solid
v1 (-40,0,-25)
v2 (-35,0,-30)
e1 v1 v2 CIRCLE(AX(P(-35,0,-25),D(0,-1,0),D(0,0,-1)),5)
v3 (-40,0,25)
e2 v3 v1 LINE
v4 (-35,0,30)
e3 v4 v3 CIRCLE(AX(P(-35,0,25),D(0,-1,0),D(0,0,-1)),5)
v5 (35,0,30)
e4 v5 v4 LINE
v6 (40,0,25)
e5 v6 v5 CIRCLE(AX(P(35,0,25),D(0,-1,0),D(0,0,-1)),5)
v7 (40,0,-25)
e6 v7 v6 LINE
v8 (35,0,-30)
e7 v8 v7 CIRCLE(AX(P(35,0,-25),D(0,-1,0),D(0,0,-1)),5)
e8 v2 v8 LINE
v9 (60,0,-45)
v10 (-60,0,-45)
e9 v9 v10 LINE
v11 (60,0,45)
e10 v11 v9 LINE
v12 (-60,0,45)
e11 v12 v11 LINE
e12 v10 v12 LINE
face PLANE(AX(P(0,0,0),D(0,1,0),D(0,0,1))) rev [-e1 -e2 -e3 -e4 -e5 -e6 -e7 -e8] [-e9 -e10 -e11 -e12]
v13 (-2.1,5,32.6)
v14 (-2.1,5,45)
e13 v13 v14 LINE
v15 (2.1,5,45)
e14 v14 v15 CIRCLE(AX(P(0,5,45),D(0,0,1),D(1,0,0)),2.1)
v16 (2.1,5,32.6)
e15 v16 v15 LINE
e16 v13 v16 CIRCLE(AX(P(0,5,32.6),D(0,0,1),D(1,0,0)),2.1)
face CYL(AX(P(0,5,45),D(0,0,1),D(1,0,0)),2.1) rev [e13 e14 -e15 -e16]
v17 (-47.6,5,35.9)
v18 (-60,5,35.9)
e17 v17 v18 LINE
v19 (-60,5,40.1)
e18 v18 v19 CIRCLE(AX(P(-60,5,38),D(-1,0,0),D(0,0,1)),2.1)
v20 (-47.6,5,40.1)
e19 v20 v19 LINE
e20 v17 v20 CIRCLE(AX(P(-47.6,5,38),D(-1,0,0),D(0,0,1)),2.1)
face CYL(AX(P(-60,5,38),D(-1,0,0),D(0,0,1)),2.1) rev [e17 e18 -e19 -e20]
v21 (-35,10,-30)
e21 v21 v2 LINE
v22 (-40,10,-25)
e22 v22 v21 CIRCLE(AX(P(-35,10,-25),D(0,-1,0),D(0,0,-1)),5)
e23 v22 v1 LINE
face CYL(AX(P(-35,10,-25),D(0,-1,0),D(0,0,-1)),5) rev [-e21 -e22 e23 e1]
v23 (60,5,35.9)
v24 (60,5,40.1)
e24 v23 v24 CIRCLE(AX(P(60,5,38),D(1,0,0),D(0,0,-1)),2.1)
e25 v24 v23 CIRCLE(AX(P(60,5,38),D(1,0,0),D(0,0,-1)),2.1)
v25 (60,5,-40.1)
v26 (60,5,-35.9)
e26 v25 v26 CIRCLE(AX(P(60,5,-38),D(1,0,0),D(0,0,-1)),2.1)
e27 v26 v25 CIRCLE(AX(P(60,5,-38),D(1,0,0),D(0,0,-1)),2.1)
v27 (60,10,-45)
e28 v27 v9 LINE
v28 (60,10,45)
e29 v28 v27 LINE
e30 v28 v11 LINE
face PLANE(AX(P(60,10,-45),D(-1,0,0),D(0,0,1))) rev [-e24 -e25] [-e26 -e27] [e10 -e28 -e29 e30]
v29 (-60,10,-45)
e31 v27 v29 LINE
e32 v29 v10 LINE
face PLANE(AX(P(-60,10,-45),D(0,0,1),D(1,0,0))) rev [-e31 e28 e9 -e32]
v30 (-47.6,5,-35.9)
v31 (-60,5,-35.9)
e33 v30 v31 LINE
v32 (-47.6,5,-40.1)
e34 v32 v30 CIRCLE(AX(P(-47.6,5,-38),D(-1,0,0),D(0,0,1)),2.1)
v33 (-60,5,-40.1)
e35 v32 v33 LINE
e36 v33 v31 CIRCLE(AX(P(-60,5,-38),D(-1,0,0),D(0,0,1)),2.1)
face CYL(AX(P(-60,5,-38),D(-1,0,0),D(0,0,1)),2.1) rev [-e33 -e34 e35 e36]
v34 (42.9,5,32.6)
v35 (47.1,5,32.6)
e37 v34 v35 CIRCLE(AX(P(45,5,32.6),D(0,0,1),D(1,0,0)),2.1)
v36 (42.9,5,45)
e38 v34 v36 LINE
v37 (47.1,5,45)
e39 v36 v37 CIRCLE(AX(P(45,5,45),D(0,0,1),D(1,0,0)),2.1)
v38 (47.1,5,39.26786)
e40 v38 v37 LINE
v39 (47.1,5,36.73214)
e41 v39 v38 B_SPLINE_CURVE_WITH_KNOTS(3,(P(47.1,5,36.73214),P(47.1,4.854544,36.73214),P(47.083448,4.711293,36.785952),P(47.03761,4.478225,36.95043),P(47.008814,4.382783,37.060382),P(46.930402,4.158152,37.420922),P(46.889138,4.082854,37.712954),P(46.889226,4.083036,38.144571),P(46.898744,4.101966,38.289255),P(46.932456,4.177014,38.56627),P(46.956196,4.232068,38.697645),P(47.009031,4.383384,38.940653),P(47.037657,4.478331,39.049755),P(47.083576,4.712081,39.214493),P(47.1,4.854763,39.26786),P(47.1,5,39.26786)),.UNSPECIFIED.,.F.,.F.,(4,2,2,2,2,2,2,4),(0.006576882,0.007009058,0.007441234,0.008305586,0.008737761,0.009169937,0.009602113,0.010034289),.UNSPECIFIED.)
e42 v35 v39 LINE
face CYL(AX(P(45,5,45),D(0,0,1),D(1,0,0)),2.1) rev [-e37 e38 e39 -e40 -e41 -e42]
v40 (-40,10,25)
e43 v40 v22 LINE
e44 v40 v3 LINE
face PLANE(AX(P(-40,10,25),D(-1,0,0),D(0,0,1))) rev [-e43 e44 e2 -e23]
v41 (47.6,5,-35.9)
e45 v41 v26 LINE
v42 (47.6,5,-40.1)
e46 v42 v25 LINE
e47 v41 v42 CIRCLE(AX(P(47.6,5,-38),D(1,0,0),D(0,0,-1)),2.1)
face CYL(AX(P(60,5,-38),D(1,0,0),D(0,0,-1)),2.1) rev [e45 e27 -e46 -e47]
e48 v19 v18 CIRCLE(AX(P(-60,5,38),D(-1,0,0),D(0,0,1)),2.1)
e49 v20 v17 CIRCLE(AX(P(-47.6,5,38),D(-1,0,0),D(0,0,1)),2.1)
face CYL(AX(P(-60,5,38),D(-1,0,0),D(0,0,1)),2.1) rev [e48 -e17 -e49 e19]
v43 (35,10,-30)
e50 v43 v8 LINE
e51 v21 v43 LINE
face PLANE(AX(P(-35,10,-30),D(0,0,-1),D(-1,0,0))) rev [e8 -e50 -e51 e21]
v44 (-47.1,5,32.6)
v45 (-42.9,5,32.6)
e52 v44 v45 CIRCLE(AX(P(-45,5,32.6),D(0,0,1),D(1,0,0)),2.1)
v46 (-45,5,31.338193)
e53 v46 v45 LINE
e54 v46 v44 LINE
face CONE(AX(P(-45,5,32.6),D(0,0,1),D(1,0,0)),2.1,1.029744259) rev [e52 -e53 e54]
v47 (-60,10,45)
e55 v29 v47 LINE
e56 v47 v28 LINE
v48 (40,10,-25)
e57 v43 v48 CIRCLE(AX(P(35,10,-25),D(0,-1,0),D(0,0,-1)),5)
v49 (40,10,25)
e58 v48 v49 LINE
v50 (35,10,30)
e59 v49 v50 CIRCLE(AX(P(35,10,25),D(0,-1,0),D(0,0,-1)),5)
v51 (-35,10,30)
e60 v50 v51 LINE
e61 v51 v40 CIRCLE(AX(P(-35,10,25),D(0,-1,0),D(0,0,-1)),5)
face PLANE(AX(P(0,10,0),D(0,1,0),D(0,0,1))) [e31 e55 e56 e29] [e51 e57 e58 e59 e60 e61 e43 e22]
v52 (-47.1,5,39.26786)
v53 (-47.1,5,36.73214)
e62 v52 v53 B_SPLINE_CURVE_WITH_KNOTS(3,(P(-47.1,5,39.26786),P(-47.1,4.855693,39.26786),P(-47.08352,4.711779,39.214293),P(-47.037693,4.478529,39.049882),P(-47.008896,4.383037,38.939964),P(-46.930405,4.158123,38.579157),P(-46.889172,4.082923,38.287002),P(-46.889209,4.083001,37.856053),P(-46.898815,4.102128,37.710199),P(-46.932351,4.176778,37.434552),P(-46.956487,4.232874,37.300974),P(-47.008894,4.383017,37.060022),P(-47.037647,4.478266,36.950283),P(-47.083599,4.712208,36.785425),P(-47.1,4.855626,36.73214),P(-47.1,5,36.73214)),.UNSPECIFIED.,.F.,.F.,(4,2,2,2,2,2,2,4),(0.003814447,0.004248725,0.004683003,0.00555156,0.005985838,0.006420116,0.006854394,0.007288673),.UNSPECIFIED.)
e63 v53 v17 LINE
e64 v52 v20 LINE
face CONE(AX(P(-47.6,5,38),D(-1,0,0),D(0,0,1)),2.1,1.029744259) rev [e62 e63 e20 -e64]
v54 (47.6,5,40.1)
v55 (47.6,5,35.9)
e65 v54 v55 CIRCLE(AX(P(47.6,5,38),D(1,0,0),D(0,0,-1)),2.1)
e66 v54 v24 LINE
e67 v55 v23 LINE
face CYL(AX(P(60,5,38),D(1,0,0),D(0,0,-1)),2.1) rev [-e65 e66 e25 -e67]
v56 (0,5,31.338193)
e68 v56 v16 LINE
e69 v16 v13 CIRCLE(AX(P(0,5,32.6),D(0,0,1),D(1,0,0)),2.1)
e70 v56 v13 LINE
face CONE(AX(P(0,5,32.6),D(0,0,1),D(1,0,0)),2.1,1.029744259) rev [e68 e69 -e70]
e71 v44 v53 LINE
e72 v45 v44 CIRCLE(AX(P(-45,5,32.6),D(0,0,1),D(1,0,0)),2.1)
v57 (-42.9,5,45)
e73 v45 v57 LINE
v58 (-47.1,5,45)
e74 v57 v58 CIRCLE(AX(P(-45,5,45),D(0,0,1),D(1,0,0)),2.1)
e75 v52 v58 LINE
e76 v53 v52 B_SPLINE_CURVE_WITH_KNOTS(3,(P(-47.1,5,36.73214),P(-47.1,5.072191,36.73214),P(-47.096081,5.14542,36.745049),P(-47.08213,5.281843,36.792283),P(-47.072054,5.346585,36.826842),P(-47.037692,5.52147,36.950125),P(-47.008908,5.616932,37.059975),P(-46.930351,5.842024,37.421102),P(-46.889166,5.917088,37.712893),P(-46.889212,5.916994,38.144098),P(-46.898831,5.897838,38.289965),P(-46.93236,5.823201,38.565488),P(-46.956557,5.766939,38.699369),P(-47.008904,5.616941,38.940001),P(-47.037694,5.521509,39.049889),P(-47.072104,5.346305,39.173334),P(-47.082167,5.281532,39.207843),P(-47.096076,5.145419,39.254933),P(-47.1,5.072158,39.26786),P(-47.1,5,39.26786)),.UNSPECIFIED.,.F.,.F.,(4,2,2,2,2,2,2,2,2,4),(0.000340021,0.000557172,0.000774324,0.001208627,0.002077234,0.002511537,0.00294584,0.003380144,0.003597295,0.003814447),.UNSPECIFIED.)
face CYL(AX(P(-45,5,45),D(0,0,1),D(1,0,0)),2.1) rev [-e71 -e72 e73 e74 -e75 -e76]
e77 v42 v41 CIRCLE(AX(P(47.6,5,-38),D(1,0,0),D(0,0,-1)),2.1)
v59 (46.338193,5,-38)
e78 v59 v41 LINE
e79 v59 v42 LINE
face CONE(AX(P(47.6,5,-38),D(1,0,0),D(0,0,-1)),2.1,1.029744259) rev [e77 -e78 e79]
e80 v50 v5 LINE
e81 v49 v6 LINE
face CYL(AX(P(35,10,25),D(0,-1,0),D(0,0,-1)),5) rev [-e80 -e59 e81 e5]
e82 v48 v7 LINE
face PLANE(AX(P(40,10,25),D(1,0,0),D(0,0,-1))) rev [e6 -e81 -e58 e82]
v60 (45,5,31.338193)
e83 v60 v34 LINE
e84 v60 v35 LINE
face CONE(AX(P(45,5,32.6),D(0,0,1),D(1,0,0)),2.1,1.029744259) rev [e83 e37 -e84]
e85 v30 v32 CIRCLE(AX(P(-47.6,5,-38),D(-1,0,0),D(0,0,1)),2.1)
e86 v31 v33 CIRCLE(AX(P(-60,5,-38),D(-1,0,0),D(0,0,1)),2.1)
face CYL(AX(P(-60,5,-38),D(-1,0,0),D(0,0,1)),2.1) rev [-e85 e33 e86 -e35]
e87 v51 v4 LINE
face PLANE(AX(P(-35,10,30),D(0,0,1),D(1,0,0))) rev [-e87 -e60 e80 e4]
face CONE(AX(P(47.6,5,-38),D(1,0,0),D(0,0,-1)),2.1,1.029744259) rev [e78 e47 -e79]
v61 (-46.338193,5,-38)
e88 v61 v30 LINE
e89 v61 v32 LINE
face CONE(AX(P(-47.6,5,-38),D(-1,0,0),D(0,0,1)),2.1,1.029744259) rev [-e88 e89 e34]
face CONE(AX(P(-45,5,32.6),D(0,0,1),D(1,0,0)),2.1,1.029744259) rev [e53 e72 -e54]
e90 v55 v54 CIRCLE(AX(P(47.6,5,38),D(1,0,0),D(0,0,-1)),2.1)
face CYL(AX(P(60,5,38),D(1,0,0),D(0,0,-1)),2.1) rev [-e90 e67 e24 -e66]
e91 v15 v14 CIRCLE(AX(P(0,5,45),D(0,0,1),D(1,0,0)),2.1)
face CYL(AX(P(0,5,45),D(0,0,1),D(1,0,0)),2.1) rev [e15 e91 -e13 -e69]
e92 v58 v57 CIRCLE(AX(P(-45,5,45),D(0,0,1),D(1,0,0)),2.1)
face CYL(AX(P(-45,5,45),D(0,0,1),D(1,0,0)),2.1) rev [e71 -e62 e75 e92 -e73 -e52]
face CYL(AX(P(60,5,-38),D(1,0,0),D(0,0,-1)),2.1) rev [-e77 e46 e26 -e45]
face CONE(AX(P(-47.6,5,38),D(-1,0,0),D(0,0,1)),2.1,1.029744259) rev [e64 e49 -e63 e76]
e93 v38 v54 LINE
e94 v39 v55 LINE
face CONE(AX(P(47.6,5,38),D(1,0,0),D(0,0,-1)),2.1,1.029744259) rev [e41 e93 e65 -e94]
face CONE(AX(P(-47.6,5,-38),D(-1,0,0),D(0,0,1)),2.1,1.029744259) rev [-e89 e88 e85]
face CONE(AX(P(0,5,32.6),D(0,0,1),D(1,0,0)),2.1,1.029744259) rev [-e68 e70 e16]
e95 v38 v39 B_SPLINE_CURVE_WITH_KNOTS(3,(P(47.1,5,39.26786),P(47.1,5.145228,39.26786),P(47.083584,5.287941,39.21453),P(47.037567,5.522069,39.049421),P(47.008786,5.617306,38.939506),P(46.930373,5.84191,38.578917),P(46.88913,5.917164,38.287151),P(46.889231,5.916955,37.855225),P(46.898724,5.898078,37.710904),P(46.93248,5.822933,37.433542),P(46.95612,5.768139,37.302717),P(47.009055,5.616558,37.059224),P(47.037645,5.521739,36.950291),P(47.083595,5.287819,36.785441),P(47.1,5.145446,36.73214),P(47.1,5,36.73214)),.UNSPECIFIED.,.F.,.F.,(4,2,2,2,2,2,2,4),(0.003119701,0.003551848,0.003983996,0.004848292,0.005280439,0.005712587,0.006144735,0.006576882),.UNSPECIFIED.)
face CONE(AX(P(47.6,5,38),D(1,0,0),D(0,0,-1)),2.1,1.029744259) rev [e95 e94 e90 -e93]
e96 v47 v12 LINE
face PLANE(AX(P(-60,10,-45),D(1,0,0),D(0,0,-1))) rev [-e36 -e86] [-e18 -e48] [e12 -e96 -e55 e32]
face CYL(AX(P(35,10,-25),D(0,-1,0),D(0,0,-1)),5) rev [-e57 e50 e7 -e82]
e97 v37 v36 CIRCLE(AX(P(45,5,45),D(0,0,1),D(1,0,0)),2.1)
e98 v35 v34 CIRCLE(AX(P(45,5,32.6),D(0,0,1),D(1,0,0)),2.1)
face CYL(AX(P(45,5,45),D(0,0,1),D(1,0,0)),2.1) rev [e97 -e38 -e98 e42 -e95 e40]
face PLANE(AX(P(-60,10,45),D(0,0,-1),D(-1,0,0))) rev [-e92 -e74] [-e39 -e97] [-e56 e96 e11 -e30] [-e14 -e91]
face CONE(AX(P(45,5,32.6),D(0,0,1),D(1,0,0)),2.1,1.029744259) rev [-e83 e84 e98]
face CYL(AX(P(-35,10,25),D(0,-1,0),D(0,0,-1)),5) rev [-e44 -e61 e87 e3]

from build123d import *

# Parameters (mm, degrees)
SKETCH1_W                  = 120
SKETCH1_H                  = 90
BOSS_EXTRUDE1_DEPTH        = 10
SKETCH2_R                  = 0.808722662
CUT_EXTRUDE1_DEPTH         = 8
M5_TAPPED_HOLE1_AT_2_COUNT = 2
M5_TAPPED_HOLE1_AT_2_PITCH = 76
SKETCH4_R                  = 1.068128835
SKETCH4_R_2                = 0.756333918
SKETCH4_R_3                = 1.055288756
CUT_EXTRUDE2_DEPTH         = 6.5
M5_TAPPED_HOLE2_D          = 4.2
M5_TAPPED_HOLE2_DEPTH      = 12.4
M5_TAPPED_HOLE2_TIP        = 1.2618073
CUT_EXTRUDE3_DEPTH         = 76.663729812


with BuildPart() as part:
    # Sketch1 → Boss-Extrude1 (new body)
    with BuildSketch(Plane(origin=(0, 0, 0), x_dir=(1, 0, 0), z_dir=(0, 1, 0))):
        Rectangle(SKETCH1_W, SKETCH1_H)
    extrude(amount=BOSS_EXTRUDE1_DEPTH)

    # Sketch2 → Cut-Extrude1 (cut)
    with BuildSketch(Plane.ZY.offset(60)):
        with Locations(Location((-38, 5, 0), (0, 0, 180))):
            Circle(SKETCH2_R)
        with Locations((38, 5)):
            Circle(SKETCH2_R)
    extrude(amount=-CUT_EXTRUDE1_DEPTH, mode=Mode.SUBTRACT)

    # Sketch3 → M5 Tapped Hole1 (revolve, cut)
    with BuildSketch(Plane(origin=(-60, 5, 38), x_dir=(0, 0, 1), z_dir=(0, 1, 0))):
        Polygon((0, 0), (0, 13.6618073), (2.1, 12.4), (2.1, 0), align=None)
    m5_tapped_hole1 = revolve(axis=Axis((-66.35, 5, 38), (1, 0, 0)), mode=Mode.SUBTRACT)

    # M5 Tapped Hole1 at 2: M5 Tapped Hole1 ×2
    with Locations(*[(0, 0, -i * M5_TAPPED_HOLE1_AT_2_PITCH) for i in range(1, M5_TAPPED_HOLE1_AT_2_COUNT)]):
        add(m5_tapped_hole1, mode=Mode.SUBTRACT)

    # Mirror1: M5 Tapped Hole1 across plane
    add(m5_tapped_hole1.mirror(Plane(origin=(0, 0, 0), x_dir=(0, 0, 1), z_dir=(1, 0, 0))), mode=Mode.SUBTRACT)

    # Mirror1 copy 1 sketch → Mirror1 copy 1 (revolve, cut)
    with BuildSketch(Plane(origin=(60, 5, -38), x_dir=(0, 0, 1), z_dir=(0, 1, 0))):
        Polygon((0, 0), (0, -13.6618073), (2.1, -12.4), (2.1, 0), align=None)
    revolve(axis=Axis((66.35, 5, -38), (1, 0, 0)), mode=Mode.SUBTRACT)

    # Sketch4 → Cut-Extrude2 (cut)
    with BuildSketch(Plane.XY.offset(45)):
        with Locations((45, 5)):
            Circle(SKETCH4_R)
        with Locations((0, 5)):
            Circle(SKETCH4_R_2)
        with Locations((-45, 5)):
            Circle(SKETCH4_R_3)
    extrude(amount=-CUT_EXTRUDE2_DEPTH, mode=Mode.SUBTRACT)

    # M5 Tapped Hole2
    with Locations(Plane(origin=(-45, 5, 45), x_dir=(1, 0, 0), z_dir=(0, 0, 1))):
        with Locations((0, 0), (45, 0), (90, 0)):
            Hole(M5_TAPPED_HOLE2_D / 2, depth=M5_TAPPED_HOLE2_DEPTH)
            with Locations((0, 0, -(M5_TAPPED_HOLE2_DEPTH + M5_TAPPED_HOLE2_TIP / 2))):  # 118° drill point
                Cone(0, M5_TAPPED_HOLE2_D / 2, M5_TAPPED_HOLE2_TIP, mode=Mode.SUBTRACT)

    # Sketch6 → Cut-Extrude3 (cut, through all)
    with BuildSketch(Plane.XZ):
        with BuildLine():
            Line((-35, 30), (35, 30))
            ThreePointArc((35, 30), (38.535533906, 28.535533906), (40, 25))
            Line((40, 25), (40, -25))
            ThreePointArc((40, -25), (38.535533906, -28.535533906), (35, -30))
            Line((35, -30), (-35, -30))
            ThreePointArc((-35, -30), (-38.535533906, -28.535533906), (-40, -25))
            Line((-40, -25), (-40, 25))
            ThreePointArc((-40, 25), (-38.535533906, 28.535533906), (-35, 30))
        make_face()
    extrude(amount=-CUT_EXTRUDE3_DEPTH, mode=Mode.SUBTRACT)


solid = part.part
